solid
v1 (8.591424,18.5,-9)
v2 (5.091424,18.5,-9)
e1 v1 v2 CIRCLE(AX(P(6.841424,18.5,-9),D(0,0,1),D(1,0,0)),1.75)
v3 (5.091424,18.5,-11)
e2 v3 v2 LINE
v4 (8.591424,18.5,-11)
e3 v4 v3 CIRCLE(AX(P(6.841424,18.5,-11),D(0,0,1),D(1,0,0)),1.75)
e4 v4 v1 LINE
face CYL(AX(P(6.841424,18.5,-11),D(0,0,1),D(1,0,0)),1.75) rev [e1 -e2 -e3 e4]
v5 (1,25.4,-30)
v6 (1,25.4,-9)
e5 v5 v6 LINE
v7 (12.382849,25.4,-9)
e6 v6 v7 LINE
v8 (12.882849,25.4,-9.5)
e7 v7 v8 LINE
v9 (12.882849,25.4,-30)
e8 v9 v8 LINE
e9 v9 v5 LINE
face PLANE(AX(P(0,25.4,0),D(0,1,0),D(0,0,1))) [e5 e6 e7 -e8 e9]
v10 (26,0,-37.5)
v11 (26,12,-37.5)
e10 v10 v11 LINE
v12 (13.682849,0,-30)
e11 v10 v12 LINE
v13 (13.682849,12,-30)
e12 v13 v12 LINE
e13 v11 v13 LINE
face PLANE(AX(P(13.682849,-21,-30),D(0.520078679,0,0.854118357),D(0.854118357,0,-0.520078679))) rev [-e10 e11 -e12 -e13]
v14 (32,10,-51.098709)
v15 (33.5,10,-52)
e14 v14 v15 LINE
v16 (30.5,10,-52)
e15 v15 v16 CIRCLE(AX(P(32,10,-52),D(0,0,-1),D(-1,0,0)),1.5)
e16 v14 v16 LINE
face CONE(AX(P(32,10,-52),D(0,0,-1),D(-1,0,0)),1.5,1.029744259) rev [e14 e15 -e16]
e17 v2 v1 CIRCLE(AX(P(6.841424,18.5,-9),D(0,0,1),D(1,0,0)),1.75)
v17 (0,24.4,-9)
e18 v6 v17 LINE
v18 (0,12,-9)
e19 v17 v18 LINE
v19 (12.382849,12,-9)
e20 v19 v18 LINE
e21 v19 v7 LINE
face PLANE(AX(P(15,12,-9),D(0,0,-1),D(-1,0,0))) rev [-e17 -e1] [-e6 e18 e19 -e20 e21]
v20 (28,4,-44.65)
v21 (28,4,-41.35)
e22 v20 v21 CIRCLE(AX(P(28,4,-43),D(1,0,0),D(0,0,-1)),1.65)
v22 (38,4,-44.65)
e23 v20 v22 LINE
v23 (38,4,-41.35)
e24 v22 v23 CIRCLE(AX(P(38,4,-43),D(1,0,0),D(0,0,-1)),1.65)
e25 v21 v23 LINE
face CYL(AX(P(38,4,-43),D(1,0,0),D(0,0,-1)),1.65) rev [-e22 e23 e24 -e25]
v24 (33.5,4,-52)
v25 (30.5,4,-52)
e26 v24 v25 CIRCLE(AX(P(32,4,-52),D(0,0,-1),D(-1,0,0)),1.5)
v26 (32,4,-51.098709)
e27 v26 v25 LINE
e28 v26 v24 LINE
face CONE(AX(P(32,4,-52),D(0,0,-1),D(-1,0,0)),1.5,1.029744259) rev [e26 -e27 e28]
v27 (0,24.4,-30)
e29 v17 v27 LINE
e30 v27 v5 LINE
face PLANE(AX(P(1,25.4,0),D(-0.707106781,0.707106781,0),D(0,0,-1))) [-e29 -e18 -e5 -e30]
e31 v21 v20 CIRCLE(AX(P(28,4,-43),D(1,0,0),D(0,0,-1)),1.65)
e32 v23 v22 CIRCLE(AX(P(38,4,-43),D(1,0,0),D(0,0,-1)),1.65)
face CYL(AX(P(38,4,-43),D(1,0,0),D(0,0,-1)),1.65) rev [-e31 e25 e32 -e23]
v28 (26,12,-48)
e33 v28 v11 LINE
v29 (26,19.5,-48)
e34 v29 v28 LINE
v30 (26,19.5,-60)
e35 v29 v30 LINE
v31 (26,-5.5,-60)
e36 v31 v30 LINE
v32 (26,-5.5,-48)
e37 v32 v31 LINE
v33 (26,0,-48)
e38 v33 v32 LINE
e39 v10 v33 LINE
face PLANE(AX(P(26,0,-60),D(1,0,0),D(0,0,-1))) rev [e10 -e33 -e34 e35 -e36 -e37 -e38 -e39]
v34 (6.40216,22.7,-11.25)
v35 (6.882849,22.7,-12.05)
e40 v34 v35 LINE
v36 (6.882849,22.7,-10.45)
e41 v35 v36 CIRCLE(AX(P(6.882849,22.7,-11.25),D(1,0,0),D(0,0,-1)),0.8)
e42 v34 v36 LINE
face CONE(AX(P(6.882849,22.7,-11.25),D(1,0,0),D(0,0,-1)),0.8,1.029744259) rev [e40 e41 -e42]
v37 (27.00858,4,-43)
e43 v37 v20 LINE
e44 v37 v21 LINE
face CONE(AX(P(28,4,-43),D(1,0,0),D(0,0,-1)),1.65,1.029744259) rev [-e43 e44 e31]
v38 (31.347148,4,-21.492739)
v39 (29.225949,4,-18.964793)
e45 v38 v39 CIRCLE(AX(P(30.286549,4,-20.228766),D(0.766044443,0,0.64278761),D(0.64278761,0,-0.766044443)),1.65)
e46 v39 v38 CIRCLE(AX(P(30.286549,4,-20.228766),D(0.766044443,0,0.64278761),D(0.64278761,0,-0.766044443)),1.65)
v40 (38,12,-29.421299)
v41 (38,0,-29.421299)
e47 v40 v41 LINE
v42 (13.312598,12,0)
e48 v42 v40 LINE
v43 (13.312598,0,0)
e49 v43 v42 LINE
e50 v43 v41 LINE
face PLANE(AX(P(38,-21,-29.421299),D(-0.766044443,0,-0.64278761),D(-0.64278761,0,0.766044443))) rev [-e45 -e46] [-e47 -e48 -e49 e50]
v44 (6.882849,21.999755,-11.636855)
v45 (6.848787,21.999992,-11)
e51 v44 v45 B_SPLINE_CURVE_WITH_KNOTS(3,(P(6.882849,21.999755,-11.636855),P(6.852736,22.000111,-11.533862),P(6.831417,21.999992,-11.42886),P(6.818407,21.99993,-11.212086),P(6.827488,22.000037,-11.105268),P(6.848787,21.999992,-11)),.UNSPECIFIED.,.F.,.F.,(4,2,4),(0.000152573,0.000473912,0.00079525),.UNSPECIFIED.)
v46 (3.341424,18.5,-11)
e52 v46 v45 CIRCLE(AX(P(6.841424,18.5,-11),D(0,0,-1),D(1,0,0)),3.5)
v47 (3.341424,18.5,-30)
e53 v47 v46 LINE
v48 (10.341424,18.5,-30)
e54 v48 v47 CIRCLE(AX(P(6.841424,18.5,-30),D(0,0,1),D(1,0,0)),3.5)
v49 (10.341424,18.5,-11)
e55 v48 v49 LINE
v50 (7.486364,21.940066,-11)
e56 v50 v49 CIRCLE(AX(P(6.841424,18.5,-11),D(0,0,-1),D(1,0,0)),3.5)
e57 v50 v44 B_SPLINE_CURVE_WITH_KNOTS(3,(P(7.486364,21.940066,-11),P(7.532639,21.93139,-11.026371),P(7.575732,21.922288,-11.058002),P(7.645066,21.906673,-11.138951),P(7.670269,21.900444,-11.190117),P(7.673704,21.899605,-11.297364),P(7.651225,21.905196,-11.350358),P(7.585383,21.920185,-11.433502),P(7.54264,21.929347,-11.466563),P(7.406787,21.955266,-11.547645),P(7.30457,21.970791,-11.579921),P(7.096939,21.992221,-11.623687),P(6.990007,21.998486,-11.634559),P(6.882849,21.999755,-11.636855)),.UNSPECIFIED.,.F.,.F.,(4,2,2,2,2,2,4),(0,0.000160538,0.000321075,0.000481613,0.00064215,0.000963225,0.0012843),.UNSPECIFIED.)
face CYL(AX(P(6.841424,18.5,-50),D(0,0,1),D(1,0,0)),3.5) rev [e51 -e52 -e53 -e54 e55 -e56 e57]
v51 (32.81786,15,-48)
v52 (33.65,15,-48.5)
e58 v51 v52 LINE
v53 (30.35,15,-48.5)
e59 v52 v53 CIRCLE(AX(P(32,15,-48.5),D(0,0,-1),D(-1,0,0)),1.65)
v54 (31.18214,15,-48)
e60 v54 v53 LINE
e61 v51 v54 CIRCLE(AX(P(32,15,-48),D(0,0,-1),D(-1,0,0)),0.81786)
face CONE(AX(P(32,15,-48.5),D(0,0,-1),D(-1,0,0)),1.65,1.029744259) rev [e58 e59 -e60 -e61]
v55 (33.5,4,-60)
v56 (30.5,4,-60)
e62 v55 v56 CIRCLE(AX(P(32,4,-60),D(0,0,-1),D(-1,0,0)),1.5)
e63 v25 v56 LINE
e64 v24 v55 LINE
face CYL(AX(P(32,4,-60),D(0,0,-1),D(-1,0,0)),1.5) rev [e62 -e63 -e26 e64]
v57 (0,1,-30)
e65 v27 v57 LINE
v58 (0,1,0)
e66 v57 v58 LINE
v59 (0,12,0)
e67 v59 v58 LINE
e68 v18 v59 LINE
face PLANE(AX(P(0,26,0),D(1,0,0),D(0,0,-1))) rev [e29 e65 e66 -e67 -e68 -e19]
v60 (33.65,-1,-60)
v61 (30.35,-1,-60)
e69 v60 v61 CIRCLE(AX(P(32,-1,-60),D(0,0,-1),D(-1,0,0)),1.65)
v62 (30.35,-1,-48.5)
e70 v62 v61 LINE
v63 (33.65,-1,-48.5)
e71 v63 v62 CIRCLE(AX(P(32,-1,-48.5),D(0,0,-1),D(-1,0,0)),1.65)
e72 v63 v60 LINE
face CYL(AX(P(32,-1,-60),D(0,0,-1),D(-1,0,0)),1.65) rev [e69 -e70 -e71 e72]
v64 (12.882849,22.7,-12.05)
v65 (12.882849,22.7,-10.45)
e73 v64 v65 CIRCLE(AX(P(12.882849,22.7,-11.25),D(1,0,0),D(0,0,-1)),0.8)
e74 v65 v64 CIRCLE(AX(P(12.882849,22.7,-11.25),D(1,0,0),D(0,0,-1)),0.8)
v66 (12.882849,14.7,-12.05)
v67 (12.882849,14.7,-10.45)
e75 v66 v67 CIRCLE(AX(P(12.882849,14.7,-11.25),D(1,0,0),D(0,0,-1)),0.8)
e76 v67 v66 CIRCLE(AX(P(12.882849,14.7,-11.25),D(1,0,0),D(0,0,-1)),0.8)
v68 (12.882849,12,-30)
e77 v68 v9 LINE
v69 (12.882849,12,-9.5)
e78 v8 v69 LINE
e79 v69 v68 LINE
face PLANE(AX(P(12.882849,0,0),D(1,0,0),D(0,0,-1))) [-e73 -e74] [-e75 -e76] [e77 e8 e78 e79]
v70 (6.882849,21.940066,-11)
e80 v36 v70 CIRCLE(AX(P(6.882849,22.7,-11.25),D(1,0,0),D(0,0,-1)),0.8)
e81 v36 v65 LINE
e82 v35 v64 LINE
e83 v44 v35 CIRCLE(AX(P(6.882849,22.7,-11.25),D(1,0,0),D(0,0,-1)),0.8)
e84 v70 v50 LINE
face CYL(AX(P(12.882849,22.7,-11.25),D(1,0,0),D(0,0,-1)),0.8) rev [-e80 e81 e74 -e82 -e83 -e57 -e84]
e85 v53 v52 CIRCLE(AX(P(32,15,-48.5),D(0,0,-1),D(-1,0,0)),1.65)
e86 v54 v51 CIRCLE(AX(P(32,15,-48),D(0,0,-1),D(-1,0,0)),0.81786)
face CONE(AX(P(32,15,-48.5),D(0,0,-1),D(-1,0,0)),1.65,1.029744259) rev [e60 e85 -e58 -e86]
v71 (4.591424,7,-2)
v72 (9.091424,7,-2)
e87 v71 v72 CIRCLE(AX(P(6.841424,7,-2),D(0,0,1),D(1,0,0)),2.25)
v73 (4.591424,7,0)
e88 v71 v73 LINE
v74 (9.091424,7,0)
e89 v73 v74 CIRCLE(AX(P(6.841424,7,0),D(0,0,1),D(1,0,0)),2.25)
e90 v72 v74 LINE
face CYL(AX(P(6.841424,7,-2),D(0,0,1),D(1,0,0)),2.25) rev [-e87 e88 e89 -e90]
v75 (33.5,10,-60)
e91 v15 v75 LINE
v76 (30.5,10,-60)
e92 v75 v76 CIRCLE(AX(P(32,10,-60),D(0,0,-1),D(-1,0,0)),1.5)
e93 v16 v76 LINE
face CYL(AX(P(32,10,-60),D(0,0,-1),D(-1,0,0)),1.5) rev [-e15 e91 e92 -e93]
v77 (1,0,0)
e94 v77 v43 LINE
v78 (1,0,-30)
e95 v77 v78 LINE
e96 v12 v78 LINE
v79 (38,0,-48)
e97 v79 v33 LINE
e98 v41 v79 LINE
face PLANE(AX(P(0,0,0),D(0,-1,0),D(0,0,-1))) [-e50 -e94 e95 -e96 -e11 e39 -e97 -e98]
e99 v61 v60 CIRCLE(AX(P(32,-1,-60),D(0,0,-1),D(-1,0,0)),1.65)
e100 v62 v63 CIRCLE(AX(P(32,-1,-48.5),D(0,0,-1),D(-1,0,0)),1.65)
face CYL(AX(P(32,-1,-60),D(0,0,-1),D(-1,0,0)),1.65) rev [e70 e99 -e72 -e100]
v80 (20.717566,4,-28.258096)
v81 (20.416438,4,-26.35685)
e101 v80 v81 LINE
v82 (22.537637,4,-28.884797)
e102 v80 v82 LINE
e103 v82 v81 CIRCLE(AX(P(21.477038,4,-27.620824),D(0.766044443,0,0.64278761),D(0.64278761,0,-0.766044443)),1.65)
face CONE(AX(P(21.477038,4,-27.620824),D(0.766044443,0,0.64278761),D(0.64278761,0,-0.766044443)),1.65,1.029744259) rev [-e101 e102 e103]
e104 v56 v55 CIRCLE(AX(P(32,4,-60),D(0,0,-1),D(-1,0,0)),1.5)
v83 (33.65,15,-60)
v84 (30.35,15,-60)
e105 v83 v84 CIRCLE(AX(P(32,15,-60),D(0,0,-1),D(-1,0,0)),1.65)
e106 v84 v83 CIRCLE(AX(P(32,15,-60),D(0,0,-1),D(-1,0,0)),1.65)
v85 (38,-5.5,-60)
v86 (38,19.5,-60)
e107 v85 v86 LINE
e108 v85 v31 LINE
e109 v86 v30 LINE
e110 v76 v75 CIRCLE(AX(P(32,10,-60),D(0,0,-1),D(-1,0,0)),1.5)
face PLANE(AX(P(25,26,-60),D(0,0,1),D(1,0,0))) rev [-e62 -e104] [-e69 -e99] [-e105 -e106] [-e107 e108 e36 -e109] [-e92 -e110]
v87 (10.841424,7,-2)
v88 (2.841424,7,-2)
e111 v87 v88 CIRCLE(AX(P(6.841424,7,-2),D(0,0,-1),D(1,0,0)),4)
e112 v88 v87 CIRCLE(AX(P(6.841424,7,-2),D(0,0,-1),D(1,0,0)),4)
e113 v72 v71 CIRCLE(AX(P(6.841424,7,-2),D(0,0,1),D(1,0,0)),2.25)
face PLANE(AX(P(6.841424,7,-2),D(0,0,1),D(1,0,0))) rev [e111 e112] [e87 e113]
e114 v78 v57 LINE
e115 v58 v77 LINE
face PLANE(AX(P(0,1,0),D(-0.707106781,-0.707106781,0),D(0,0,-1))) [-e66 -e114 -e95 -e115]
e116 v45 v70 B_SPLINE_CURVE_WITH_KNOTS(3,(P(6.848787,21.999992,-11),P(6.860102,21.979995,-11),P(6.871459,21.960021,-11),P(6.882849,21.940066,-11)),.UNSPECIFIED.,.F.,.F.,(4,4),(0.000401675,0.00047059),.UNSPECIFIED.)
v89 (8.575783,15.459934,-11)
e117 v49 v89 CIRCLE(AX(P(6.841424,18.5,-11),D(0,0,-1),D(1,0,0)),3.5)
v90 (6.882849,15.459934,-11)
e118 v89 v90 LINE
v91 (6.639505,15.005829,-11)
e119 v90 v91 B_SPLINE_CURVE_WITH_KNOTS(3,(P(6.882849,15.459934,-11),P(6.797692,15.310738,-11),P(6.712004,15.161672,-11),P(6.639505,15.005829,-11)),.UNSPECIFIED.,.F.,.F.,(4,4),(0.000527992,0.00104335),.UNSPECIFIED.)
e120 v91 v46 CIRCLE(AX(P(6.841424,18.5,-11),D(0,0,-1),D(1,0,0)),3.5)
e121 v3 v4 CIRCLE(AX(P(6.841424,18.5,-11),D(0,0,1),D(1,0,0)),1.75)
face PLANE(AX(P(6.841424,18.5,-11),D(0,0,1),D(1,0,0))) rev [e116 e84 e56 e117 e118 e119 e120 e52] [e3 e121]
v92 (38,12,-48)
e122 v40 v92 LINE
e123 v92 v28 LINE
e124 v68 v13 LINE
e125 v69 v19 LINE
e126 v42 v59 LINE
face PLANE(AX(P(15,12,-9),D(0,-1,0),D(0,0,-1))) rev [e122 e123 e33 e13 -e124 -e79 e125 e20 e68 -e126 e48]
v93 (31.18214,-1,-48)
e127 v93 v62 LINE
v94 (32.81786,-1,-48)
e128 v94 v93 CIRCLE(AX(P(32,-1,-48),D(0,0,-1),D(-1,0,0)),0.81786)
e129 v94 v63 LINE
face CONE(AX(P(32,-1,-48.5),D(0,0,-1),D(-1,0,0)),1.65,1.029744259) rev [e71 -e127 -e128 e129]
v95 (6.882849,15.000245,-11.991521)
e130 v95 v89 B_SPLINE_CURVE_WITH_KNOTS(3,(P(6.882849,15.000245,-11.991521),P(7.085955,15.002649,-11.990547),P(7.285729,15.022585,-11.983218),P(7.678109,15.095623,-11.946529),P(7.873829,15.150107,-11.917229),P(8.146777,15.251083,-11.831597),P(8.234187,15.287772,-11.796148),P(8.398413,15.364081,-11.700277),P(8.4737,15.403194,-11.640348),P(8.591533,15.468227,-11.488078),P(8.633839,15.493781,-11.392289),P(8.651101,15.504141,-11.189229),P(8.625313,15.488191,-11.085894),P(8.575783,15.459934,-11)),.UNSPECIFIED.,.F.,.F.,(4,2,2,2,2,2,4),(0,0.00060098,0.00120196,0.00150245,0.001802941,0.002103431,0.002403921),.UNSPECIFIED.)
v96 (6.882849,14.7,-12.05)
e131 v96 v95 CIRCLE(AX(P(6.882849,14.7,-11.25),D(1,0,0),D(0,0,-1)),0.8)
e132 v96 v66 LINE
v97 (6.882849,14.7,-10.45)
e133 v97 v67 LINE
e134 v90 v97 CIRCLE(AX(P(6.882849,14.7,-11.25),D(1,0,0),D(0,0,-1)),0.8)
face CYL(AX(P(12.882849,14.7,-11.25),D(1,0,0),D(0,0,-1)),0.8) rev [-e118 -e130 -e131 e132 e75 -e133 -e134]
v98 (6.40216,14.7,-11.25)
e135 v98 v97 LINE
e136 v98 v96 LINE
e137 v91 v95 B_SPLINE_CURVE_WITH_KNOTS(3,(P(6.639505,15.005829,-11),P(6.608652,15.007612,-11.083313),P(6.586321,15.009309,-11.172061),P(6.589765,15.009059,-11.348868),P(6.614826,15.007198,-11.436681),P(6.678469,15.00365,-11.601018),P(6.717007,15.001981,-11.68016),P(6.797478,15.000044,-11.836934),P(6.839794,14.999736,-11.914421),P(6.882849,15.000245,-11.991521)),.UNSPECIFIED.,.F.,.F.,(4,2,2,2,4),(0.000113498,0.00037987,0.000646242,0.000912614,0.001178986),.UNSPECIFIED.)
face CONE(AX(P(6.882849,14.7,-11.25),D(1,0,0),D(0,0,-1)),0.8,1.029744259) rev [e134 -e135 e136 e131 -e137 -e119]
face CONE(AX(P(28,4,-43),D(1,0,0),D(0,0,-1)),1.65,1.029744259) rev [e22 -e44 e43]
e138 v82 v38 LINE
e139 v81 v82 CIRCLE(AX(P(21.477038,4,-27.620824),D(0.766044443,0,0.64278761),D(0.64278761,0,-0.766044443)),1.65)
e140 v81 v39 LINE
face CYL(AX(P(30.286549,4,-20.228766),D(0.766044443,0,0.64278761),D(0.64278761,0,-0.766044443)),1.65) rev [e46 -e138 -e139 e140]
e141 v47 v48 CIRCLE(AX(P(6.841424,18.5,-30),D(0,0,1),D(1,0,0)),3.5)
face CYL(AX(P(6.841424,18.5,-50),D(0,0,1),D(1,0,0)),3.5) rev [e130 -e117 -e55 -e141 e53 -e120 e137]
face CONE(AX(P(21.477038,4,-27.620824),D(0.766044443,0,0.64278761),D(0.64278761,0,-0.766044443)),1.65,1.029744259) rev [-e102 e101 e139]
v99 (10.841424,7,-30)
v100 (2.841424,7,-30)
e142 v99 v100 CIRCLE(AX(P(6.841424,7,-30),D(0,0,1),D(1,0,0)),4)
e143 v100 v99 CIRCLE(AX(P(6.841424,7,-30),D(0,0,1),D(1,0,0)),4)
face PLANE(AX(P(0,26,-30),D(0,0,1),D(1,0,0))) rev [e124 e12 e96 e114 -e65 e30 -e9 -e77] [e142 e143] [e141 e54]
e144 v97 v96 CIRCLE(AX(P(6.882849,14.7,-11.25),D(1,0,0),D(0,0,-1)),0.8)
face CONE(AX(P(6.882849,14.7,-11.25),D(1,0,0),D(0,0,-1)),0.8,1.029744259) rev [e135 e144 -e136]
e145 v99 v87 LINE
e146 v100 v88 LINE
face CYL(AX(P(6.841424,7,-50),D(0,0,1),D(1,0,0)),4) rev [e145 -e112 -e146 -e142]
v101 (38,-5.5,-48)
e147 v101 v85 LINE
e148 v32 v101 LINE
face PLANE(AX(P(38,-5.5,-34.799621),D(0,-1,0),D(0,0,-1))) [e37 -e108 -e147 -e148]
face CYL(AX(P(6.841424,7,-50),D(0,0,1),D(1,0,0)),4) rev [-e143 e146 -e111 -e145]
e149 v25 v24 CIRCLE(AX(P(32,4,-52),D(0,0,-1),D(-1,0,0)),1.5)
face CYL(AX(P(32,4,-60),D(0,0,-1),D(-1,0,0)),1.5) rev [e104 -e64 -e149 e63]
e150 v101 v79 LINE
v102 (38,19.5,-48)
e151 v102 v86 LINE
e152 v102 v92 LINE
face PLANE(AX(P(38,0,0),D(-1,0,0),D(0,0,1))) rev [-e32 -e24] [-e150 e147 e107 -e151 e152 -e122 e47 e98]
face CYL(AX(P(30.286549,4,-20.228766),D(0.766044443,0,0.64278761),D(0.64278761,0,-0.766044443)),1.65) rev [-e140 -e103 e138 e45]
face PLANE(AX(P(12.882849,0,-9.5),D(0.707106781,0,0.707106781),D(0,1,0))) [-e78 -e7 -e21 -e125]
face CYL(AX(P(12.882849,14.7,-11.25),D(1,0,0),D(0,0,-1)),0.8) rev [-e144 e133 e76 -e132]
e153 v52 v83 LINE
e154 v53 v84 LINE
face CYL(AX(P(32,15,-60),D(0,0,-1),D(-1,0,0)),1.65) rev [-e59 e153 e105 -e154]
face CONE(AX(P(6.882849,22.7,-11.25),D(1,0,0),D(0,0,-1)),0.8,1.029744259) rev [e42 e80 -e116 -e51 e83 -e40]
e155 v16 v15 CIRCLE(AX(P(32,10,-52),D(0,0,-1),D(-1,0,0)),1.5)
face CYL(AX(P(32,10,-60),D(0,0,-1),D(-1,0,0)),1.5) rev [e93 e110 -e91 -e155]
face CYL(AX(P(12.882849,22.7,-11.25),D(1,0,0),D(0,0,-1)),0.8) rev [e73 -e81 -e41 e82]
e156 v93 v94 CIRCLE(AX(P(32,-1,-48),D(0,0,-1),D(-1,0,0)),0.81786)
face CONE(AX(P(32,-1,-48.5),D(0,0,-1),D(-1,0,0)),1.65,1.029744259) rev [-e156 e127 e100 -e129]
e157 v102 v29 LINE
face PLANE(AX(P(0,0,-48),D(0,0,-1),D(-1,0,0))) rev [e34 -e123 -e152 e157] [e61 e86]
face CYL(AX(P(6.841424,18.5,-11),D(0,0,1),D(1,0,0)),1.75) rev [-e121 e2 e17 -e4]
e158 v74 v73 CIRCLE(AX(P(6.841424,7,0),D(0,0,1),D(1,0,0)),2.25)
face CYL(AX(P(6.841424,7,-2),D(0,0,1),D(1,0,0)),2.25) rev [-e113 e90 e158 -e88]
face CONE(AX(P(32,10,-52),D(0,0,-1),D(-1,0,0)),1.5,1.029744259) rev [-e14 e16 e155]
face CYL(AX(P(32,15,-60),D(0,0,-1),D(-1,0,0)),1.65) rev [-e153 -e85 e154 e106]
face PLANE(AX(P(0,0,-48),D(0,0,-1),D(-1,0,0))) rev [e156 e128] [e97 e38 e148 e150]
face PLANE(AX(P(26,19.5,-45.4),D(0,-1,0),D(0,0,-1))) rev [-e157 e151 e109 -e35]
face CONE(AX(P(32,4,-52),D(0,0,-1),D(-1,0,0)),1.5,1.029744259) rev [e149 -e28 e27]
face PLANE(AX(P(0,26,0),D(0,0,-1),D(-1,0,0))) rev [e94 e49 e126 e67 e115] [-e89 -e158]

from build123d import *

# Parameters (mm, degrees)
BOSS_EXTRUDE1_DEPTH          = 26
SKETCH2_W                    = 36.317151105
SKETCH2_H                    = 12
CUT_EXTRUDE1_DEPTH           = 77
SKETCH3_R                    = 4
SKETCH3_R_2                  = 3.5
CUT_EXTRUDE2_DEPTH           = 50
SKETCH4_R                    = 4
SKETCH4_R_2                  = 2.25
BOSS_EXTRUDE2_DEPTH          = 2
SKETCH5_W                    = 9
SKETCH5_H                    = 21.000830638
CUT_EXTRUDE3_DEPTH           = 15
SKETCH6_R                    = 3.5
SKETCH6_R_2                  = 1.75
BOSS_EXTRUDE3_DEPTH          = 2
SKETCH10_W                   = 14.150971585
SKETCH10_H                   = 19.243046766
CUT_EXTRUDE4_DEPTH           = 60
SKETCH12_W                   = 13
SKETCH12_H                   = 24
BOSS_EXTRUDE6_DEPTH          = 12
SKETCH13_W                   = 1
SKETCH13_H                   = 22.5
CUT_EXTRUDE6_DEPTH           = 75.966659256
CUT_EXTRUDE7_DEPTH           = 35
CUT_EXTRUDE10_DEPTH          = 2
SKETCH19_W                   = 12
SKETCH19_H                   = 5.5
BOSS_EXTRUDE7_DEPTH          = 12
SKETCH20_W                   = 12
SKETCH20_H                   = 4.5
CUT_EXTRUDE11_DEPTH          = 14.6
SKETCH7_W                    = 13.682848895
SKETCH7_H                    = 21
CUT_EXTRUDE9_DEPTH           = 0.6
SKETCH21_W                   = 21
SKETCH21_H                   = 13.4
CUT_EXTRUDE12_DEPTH          = 0.8
M4_TAPPED_HOLE1_D            = 3.3
M4_TAPPED_HOLE1_DEPTH        = 11.5
M4_TAPPED_HOLE1_TIP          = 0.991420021
M2_TAPPED_HOLE1_D            = 1.6
M2_TAPPED_HOLE1_DEPTH        = 6
M2_TAPPED_HOLE1_TIP          = 0.480688495
F_3_0_3_DIAMETER_HOLE1_D     = 3
F_3_0_3_DIAMETER_HOLE1_DEPTH = 8
F_3_0_3_DIAMETER_HOLE1_TIP   = 0.901290929
CHAMFER1_SIZE                = 0.5
M4_TAPPED_HOLE2_D            = 3.3
M4_TAPPED_HOLE2_DEPTH        = 10
M4_TAPPED_HOLE2_TIP          = 0.991420021
M4_TAPPED_HOLE3_D            = 3.3
M4_TAPPED_HOLE3_DEPTH        = 11.5
M4_TAPPED_HOLE3_TIP          = 0.991420021
CHAMFER2_SIZE                = 1


with BuildPart() as part:
    # Sketch1 → Boss-Extrude1 (new body)
    with BuildSketch(Plane(origin=(0, 0, 0), x_dir=(1, 0, 0), z_dir=(0, 1, 0))):
        Polygon((24, 0), (50, 40), (50, 60), (25, 60), (25, 47.4110017), (13.682848895, 30), (0, 30), (0, 0), align=None)
    extrude(amount=BOSS_EXTRUDE1_DEPTH)

    # Sketch2 → Cut-Extrude1 (cut)
    with BuildSketch(Plane(origin=(0, 0, -60), x_dir=(-1, 0, 0), z_dir=(0, 0, -1))):
        with Locations((-31.841424447, 20)):
            Rectangle(SKETCH2_W, SKETCH2_H)
    extrude(amount=-CUT_EXTRUDE1_DEPTH, mode=Mode.SUBTRACT)

    # Sketch3 → Cut-Extrude2 (cut)
    with BuildSketch(Plane.XY):
        with Locations((6.841424448, 7)):
            Circle(SKETCH3_R)
        with Locations((6.841424448, 18.5)):
            Circle(SKETCH3_R_2)
    extrude(amount=-CUT_EXTRUDE2_DEPTH, mode=Mode.SUBTRACT)

    # Sketch4 → Boss-Extrude2 (add)
    with BuildSketch(Plane.XY):
        with Locations((6.841424448, 7)):
            Circle(SKETCH4_R)
        with Locations((6.841424448, 7)):
            Circle(SKETCH4_R_2, mode=Mode.SUBTRACT)
    extrude(amount=-BOSS_EXTRUDE2_DEPTH)

    # Sketch5 → Cut-Extrude3 (cut)
    with BuildSketch(Plane.ZY):
        with Locations((-4.5, 22.500415319)):
            Rectangle(SKETCH5_W, SKETCH5_H)
    extrude(amount=-CUT_EXTRUDE3_DEPTH, mode=Mode.SUBTRACT)

    # Sketch6 → Boss-Extrude3 (add)
    with BuildSketch(Plane.XY.offset(-9)):
        with Locations((6.841424448, 18.5)):
            Circle(SKETCH6_R)
        with Locations((6.841424448, 18.5)):
            Circle(SKETCH6_R_2, mode=Mode.SUBTRACT)
    extrude(amount=-BOSS_EXTRUDE3_DEPTH)

    # Sketch10 → Cut-Extrude4 (cut)
    with BuildSketch(Plane(origin=(0, 0, -60), x_dir=(-1, 0, 0), z_dir=(0, 0, -1))):
        with Locations((-45.075485793, 9.621523383)):
            Rectangle(SKETCH10_W, SKETCH10_H)
    extrude(amount=-CUT_EXTRUDE4_DEPTH, mode=Mode.SUBTRACT)

    # Sketch12 → Boss-Extrude6 (add)
    with BuildSketch(Plane(origin=(0, 0, -60), x_dir=(-1, 0, 0), z_dir=(0, 0, -1))):
        with Locations((-31.5, 12)):
            Rectangle(SKETCH12_W, SKETCH12_H)
    extrude(amount=-BOSS_EXTRUDE6_DEPTH)

    # Sketch13 → Cut-Extrude6 (cut, through all)
    with BuildSketch(Plane(origin=(0, 24, 0), x_dir=(1, 0, 0), z_dir=(0, 1, 0))):
        with Locations((25.5, 48.75)):
            Rectangle(SKETCH13_W, SKETCH13_H)
    extrude(amount=-CUT_EXTRUDE6_DEPTH, mode=Mode.SUBTRACT)

    # Sketch15 → Cut-Extrude7 (cut)
    with BuildSketch(Plane(origin=(0, 14, 0), x_dir=(1, 0, 0), z_dir=(0, 1, 0))):
        Polygon((13.682848895, 30), (26, 37.5), (26, 50.957252655), (13.682848895, 50.957252655), align=None)
        Polygon((13.312598457, 0), (38, 0), (38, 29.42129948), align=None)
    extrude(amount=-CUT_EXTRUDE7_DEPTH, mode=Mode.SUBTRACT)

    # Sketch18 → Cut-Extrude10 (cut)
    with BuildSketch(Plane(origin=(0, 14, 0), x_dir=(1, 0, 0), z_dir=(0, 1, 0))):
        Polygon((26, 48), (38, 48), (38, 29.42129948), (13.682848895, 0.44124729), (13.682848895, 30), (26, 37.5), align=None)
    extrude(amount=-CUT_EXTRUDE10_DEPTH, mode=Mode.SUBTRACT)

    # Sketch19 → Boss-Extrude7 (add)
    with BuildSketch(Plane(origin=(0, 0, -60), x_dir=(-1, 0, 0), z_dir=(0, 0, -1))):
        with Locations((-32, -2.75)):
            Rectangle(SKETCH19_W, SKETCH19_H)
    extrude(amount=-BOSS_EXTRUDE7_DEPTH)

    # Sketch20 → Cut-Extrude11 (cut)
    with BuildSketch(Plane(origin=(0, 0, -60), x_dir=(-1, 0, 0), z_dir=(0, 0, -1))):
        with Locations((-32, 21.75)):
            Rectangle(SKETCH20_W, SKETCH20_H)
    extrude(amount=-CUT_EXTRUDE11_DEPTH, mode=Mode.SUBTRACT)

    # Sketch7 → Cut-Extrude9 (cut)
    with BuildSketch(Plane(origin=(0, 26, 0), x_dir=(1, 0, 0), z_dir=(0, 1, 0))):
        with Locations((6.841424448, 19.5)):
            Rectangle(SKETCH7_W, SKETCH7_H)
    extrude(amount=-CUT_EXTRUDE9_DEPTH, mode=Mode.SUBTRACT)

    # Sketch21 → Cut-Extrude12 (cut)
    with BuildSketch(Plane(origin=(13.682848895, 0, 0), x_dir=(0, 0, -1), z_dir=(1, 0, 0))):
        with Locations((19.5, 18.7)):
            Rectangle(SKETCH21_W, SKETCH21_H)
    extrude(amount=-CUT_EXTRUDE12_DEPTH, mode=Mode.SUBTRACT)

    # M4 Tapped Hole1
    with Locations(Plane(origin=(0, 0, -60), x_dir=(-1, 0, 0), z_dir=(0, 0, -1))):
        with Locations((-32, 15), (-32, -1)):
            Hole(M4_TAPPED_HOLE1_D / 2, depth=M4_TAPPED_HOLE1_DEPTH)
            with Locations((0, 0, -(M4_TAPPED_HOLE1_DEPTH + M4_TAPPED_HOLE1_TIP / 2))):  # 118° drill point
                Cone(0, M4_TAPPED_HOLE1_D / 2, M4_TAPPED_HOLE1_TIP, mode=Mode.SUBTRACT)

    # M2 Tapped Hole1
    with Locations(Plane(origin=(12.882848895, 0, 0), x_dir=(0, 0, -1), z_dir=(1, 0, 0))):
        with Locations((11.25, 14.7), (11.25, 22.7)):
            Hole(M2_TAPPED_HOLE1_D / 2, depth=M2_TAPPED_HOLE1_DEPTH)
            with Locations((0, 0, -(M2_TAPPED_HOLE1_DEPTH + M2_TAPPED_HOLE1_TIP / 2))):  # 118° drill point
                Cone(0, M2_TAPPED_HOLE1_D / 2, M2_TAPPED_HOLE1_TIP, mode=Mode.SUBTRACT)

    # Ø3.0 (3) Diameter Hole1
    with Locations(Plane(origin=(0, 0, -60), x_dir=(-1, 0, 0), z_dir=(0, 0, -1))):
        with Locations((-32, 10), (-32, 4)):
            Hole(F_3_0_3_DIAMETER_HOLE1_D / 2, depth=F_3_0_3_DIAMETER_HOLE1_DEPTH)
            with Locations((0, 0, -(F_3_0_3_DIAMETER_HOLE1_DEPTH + F_3_0_3_DIAMETER_HOLE1_TIP / 2))):  # 118° drill point
                Cone(0, F_3_0_3_DIAMETER_HOLE1_D / 2, F_3_0_3_DIAMETER_HOLE1_TIP, mode=Mode.SUBTRACT)

    # Chamfer1
    chamfer1_edges = [part.edges().sort_by_distance(p)[0] for p in [
        (12.882848895, 18.7, -9),
    ]]
    chamfer(chamfer1_edges, length=CHAMFER1_SIZE)

    # M4 Tapped Hole2
    with Locations(Plane(origin=(38, 0, 0), x_dir=(0, 0, -1), z_dir=(1, 0, 0))):
        with Locations((43, 4)):
            Hole(M4_TAPPED_HOLE2_D / 2, depth=M4_TAPPED_HOLE2_DEPTH)
            with Locations((0, 0, -(M4_TAPPED_HOLE2_DEPTH + M4_TAPPED_HOLE2_TIP / 2))):  # 118° drill point
                Cone(0, M4_TAPPED_HOLE2_D / 2, M4_TAPPED_HOLE2_TIP, mode=Mode.SUBTRACT)

    # M4 Tapped Hole3
    with Locations(Plane(origin=(7.81215346, 0, 6.555175087), x_dir=(0.6427876096865373, 0, -0.7660444431189798), z_dir=(0.7660444431189798, 0, 0.6427876096865373))):
        with Locations((34.963952144, 4)):
            Hole(M4_TAPPED_HOLE3_D / 2, depth=M4_TAPPED_HOLE3_DEPTH)
            with Locations((0, 0, -(M4_TAPPED_HOLE3_DEPTH + M4_TAPPED_HOLE3_TIP / 2))):  # 118° drill point
                Cone(0, M4_TAPPED_HOLE3_D / 2, M4_TAPPED_HOLE3_TIP, mode=Mode.SUBTRACT)

    # Chamfer2
    chamfer2_edges = [part.edges().sort_by_distance(p)[0] for p in [
        (0, 0, -15),
        (0, 25.4, -19.5),
    ]]
    chamfer(chamfer2_edges, length=CHAMFER2_SIZE)


solid = part.part
